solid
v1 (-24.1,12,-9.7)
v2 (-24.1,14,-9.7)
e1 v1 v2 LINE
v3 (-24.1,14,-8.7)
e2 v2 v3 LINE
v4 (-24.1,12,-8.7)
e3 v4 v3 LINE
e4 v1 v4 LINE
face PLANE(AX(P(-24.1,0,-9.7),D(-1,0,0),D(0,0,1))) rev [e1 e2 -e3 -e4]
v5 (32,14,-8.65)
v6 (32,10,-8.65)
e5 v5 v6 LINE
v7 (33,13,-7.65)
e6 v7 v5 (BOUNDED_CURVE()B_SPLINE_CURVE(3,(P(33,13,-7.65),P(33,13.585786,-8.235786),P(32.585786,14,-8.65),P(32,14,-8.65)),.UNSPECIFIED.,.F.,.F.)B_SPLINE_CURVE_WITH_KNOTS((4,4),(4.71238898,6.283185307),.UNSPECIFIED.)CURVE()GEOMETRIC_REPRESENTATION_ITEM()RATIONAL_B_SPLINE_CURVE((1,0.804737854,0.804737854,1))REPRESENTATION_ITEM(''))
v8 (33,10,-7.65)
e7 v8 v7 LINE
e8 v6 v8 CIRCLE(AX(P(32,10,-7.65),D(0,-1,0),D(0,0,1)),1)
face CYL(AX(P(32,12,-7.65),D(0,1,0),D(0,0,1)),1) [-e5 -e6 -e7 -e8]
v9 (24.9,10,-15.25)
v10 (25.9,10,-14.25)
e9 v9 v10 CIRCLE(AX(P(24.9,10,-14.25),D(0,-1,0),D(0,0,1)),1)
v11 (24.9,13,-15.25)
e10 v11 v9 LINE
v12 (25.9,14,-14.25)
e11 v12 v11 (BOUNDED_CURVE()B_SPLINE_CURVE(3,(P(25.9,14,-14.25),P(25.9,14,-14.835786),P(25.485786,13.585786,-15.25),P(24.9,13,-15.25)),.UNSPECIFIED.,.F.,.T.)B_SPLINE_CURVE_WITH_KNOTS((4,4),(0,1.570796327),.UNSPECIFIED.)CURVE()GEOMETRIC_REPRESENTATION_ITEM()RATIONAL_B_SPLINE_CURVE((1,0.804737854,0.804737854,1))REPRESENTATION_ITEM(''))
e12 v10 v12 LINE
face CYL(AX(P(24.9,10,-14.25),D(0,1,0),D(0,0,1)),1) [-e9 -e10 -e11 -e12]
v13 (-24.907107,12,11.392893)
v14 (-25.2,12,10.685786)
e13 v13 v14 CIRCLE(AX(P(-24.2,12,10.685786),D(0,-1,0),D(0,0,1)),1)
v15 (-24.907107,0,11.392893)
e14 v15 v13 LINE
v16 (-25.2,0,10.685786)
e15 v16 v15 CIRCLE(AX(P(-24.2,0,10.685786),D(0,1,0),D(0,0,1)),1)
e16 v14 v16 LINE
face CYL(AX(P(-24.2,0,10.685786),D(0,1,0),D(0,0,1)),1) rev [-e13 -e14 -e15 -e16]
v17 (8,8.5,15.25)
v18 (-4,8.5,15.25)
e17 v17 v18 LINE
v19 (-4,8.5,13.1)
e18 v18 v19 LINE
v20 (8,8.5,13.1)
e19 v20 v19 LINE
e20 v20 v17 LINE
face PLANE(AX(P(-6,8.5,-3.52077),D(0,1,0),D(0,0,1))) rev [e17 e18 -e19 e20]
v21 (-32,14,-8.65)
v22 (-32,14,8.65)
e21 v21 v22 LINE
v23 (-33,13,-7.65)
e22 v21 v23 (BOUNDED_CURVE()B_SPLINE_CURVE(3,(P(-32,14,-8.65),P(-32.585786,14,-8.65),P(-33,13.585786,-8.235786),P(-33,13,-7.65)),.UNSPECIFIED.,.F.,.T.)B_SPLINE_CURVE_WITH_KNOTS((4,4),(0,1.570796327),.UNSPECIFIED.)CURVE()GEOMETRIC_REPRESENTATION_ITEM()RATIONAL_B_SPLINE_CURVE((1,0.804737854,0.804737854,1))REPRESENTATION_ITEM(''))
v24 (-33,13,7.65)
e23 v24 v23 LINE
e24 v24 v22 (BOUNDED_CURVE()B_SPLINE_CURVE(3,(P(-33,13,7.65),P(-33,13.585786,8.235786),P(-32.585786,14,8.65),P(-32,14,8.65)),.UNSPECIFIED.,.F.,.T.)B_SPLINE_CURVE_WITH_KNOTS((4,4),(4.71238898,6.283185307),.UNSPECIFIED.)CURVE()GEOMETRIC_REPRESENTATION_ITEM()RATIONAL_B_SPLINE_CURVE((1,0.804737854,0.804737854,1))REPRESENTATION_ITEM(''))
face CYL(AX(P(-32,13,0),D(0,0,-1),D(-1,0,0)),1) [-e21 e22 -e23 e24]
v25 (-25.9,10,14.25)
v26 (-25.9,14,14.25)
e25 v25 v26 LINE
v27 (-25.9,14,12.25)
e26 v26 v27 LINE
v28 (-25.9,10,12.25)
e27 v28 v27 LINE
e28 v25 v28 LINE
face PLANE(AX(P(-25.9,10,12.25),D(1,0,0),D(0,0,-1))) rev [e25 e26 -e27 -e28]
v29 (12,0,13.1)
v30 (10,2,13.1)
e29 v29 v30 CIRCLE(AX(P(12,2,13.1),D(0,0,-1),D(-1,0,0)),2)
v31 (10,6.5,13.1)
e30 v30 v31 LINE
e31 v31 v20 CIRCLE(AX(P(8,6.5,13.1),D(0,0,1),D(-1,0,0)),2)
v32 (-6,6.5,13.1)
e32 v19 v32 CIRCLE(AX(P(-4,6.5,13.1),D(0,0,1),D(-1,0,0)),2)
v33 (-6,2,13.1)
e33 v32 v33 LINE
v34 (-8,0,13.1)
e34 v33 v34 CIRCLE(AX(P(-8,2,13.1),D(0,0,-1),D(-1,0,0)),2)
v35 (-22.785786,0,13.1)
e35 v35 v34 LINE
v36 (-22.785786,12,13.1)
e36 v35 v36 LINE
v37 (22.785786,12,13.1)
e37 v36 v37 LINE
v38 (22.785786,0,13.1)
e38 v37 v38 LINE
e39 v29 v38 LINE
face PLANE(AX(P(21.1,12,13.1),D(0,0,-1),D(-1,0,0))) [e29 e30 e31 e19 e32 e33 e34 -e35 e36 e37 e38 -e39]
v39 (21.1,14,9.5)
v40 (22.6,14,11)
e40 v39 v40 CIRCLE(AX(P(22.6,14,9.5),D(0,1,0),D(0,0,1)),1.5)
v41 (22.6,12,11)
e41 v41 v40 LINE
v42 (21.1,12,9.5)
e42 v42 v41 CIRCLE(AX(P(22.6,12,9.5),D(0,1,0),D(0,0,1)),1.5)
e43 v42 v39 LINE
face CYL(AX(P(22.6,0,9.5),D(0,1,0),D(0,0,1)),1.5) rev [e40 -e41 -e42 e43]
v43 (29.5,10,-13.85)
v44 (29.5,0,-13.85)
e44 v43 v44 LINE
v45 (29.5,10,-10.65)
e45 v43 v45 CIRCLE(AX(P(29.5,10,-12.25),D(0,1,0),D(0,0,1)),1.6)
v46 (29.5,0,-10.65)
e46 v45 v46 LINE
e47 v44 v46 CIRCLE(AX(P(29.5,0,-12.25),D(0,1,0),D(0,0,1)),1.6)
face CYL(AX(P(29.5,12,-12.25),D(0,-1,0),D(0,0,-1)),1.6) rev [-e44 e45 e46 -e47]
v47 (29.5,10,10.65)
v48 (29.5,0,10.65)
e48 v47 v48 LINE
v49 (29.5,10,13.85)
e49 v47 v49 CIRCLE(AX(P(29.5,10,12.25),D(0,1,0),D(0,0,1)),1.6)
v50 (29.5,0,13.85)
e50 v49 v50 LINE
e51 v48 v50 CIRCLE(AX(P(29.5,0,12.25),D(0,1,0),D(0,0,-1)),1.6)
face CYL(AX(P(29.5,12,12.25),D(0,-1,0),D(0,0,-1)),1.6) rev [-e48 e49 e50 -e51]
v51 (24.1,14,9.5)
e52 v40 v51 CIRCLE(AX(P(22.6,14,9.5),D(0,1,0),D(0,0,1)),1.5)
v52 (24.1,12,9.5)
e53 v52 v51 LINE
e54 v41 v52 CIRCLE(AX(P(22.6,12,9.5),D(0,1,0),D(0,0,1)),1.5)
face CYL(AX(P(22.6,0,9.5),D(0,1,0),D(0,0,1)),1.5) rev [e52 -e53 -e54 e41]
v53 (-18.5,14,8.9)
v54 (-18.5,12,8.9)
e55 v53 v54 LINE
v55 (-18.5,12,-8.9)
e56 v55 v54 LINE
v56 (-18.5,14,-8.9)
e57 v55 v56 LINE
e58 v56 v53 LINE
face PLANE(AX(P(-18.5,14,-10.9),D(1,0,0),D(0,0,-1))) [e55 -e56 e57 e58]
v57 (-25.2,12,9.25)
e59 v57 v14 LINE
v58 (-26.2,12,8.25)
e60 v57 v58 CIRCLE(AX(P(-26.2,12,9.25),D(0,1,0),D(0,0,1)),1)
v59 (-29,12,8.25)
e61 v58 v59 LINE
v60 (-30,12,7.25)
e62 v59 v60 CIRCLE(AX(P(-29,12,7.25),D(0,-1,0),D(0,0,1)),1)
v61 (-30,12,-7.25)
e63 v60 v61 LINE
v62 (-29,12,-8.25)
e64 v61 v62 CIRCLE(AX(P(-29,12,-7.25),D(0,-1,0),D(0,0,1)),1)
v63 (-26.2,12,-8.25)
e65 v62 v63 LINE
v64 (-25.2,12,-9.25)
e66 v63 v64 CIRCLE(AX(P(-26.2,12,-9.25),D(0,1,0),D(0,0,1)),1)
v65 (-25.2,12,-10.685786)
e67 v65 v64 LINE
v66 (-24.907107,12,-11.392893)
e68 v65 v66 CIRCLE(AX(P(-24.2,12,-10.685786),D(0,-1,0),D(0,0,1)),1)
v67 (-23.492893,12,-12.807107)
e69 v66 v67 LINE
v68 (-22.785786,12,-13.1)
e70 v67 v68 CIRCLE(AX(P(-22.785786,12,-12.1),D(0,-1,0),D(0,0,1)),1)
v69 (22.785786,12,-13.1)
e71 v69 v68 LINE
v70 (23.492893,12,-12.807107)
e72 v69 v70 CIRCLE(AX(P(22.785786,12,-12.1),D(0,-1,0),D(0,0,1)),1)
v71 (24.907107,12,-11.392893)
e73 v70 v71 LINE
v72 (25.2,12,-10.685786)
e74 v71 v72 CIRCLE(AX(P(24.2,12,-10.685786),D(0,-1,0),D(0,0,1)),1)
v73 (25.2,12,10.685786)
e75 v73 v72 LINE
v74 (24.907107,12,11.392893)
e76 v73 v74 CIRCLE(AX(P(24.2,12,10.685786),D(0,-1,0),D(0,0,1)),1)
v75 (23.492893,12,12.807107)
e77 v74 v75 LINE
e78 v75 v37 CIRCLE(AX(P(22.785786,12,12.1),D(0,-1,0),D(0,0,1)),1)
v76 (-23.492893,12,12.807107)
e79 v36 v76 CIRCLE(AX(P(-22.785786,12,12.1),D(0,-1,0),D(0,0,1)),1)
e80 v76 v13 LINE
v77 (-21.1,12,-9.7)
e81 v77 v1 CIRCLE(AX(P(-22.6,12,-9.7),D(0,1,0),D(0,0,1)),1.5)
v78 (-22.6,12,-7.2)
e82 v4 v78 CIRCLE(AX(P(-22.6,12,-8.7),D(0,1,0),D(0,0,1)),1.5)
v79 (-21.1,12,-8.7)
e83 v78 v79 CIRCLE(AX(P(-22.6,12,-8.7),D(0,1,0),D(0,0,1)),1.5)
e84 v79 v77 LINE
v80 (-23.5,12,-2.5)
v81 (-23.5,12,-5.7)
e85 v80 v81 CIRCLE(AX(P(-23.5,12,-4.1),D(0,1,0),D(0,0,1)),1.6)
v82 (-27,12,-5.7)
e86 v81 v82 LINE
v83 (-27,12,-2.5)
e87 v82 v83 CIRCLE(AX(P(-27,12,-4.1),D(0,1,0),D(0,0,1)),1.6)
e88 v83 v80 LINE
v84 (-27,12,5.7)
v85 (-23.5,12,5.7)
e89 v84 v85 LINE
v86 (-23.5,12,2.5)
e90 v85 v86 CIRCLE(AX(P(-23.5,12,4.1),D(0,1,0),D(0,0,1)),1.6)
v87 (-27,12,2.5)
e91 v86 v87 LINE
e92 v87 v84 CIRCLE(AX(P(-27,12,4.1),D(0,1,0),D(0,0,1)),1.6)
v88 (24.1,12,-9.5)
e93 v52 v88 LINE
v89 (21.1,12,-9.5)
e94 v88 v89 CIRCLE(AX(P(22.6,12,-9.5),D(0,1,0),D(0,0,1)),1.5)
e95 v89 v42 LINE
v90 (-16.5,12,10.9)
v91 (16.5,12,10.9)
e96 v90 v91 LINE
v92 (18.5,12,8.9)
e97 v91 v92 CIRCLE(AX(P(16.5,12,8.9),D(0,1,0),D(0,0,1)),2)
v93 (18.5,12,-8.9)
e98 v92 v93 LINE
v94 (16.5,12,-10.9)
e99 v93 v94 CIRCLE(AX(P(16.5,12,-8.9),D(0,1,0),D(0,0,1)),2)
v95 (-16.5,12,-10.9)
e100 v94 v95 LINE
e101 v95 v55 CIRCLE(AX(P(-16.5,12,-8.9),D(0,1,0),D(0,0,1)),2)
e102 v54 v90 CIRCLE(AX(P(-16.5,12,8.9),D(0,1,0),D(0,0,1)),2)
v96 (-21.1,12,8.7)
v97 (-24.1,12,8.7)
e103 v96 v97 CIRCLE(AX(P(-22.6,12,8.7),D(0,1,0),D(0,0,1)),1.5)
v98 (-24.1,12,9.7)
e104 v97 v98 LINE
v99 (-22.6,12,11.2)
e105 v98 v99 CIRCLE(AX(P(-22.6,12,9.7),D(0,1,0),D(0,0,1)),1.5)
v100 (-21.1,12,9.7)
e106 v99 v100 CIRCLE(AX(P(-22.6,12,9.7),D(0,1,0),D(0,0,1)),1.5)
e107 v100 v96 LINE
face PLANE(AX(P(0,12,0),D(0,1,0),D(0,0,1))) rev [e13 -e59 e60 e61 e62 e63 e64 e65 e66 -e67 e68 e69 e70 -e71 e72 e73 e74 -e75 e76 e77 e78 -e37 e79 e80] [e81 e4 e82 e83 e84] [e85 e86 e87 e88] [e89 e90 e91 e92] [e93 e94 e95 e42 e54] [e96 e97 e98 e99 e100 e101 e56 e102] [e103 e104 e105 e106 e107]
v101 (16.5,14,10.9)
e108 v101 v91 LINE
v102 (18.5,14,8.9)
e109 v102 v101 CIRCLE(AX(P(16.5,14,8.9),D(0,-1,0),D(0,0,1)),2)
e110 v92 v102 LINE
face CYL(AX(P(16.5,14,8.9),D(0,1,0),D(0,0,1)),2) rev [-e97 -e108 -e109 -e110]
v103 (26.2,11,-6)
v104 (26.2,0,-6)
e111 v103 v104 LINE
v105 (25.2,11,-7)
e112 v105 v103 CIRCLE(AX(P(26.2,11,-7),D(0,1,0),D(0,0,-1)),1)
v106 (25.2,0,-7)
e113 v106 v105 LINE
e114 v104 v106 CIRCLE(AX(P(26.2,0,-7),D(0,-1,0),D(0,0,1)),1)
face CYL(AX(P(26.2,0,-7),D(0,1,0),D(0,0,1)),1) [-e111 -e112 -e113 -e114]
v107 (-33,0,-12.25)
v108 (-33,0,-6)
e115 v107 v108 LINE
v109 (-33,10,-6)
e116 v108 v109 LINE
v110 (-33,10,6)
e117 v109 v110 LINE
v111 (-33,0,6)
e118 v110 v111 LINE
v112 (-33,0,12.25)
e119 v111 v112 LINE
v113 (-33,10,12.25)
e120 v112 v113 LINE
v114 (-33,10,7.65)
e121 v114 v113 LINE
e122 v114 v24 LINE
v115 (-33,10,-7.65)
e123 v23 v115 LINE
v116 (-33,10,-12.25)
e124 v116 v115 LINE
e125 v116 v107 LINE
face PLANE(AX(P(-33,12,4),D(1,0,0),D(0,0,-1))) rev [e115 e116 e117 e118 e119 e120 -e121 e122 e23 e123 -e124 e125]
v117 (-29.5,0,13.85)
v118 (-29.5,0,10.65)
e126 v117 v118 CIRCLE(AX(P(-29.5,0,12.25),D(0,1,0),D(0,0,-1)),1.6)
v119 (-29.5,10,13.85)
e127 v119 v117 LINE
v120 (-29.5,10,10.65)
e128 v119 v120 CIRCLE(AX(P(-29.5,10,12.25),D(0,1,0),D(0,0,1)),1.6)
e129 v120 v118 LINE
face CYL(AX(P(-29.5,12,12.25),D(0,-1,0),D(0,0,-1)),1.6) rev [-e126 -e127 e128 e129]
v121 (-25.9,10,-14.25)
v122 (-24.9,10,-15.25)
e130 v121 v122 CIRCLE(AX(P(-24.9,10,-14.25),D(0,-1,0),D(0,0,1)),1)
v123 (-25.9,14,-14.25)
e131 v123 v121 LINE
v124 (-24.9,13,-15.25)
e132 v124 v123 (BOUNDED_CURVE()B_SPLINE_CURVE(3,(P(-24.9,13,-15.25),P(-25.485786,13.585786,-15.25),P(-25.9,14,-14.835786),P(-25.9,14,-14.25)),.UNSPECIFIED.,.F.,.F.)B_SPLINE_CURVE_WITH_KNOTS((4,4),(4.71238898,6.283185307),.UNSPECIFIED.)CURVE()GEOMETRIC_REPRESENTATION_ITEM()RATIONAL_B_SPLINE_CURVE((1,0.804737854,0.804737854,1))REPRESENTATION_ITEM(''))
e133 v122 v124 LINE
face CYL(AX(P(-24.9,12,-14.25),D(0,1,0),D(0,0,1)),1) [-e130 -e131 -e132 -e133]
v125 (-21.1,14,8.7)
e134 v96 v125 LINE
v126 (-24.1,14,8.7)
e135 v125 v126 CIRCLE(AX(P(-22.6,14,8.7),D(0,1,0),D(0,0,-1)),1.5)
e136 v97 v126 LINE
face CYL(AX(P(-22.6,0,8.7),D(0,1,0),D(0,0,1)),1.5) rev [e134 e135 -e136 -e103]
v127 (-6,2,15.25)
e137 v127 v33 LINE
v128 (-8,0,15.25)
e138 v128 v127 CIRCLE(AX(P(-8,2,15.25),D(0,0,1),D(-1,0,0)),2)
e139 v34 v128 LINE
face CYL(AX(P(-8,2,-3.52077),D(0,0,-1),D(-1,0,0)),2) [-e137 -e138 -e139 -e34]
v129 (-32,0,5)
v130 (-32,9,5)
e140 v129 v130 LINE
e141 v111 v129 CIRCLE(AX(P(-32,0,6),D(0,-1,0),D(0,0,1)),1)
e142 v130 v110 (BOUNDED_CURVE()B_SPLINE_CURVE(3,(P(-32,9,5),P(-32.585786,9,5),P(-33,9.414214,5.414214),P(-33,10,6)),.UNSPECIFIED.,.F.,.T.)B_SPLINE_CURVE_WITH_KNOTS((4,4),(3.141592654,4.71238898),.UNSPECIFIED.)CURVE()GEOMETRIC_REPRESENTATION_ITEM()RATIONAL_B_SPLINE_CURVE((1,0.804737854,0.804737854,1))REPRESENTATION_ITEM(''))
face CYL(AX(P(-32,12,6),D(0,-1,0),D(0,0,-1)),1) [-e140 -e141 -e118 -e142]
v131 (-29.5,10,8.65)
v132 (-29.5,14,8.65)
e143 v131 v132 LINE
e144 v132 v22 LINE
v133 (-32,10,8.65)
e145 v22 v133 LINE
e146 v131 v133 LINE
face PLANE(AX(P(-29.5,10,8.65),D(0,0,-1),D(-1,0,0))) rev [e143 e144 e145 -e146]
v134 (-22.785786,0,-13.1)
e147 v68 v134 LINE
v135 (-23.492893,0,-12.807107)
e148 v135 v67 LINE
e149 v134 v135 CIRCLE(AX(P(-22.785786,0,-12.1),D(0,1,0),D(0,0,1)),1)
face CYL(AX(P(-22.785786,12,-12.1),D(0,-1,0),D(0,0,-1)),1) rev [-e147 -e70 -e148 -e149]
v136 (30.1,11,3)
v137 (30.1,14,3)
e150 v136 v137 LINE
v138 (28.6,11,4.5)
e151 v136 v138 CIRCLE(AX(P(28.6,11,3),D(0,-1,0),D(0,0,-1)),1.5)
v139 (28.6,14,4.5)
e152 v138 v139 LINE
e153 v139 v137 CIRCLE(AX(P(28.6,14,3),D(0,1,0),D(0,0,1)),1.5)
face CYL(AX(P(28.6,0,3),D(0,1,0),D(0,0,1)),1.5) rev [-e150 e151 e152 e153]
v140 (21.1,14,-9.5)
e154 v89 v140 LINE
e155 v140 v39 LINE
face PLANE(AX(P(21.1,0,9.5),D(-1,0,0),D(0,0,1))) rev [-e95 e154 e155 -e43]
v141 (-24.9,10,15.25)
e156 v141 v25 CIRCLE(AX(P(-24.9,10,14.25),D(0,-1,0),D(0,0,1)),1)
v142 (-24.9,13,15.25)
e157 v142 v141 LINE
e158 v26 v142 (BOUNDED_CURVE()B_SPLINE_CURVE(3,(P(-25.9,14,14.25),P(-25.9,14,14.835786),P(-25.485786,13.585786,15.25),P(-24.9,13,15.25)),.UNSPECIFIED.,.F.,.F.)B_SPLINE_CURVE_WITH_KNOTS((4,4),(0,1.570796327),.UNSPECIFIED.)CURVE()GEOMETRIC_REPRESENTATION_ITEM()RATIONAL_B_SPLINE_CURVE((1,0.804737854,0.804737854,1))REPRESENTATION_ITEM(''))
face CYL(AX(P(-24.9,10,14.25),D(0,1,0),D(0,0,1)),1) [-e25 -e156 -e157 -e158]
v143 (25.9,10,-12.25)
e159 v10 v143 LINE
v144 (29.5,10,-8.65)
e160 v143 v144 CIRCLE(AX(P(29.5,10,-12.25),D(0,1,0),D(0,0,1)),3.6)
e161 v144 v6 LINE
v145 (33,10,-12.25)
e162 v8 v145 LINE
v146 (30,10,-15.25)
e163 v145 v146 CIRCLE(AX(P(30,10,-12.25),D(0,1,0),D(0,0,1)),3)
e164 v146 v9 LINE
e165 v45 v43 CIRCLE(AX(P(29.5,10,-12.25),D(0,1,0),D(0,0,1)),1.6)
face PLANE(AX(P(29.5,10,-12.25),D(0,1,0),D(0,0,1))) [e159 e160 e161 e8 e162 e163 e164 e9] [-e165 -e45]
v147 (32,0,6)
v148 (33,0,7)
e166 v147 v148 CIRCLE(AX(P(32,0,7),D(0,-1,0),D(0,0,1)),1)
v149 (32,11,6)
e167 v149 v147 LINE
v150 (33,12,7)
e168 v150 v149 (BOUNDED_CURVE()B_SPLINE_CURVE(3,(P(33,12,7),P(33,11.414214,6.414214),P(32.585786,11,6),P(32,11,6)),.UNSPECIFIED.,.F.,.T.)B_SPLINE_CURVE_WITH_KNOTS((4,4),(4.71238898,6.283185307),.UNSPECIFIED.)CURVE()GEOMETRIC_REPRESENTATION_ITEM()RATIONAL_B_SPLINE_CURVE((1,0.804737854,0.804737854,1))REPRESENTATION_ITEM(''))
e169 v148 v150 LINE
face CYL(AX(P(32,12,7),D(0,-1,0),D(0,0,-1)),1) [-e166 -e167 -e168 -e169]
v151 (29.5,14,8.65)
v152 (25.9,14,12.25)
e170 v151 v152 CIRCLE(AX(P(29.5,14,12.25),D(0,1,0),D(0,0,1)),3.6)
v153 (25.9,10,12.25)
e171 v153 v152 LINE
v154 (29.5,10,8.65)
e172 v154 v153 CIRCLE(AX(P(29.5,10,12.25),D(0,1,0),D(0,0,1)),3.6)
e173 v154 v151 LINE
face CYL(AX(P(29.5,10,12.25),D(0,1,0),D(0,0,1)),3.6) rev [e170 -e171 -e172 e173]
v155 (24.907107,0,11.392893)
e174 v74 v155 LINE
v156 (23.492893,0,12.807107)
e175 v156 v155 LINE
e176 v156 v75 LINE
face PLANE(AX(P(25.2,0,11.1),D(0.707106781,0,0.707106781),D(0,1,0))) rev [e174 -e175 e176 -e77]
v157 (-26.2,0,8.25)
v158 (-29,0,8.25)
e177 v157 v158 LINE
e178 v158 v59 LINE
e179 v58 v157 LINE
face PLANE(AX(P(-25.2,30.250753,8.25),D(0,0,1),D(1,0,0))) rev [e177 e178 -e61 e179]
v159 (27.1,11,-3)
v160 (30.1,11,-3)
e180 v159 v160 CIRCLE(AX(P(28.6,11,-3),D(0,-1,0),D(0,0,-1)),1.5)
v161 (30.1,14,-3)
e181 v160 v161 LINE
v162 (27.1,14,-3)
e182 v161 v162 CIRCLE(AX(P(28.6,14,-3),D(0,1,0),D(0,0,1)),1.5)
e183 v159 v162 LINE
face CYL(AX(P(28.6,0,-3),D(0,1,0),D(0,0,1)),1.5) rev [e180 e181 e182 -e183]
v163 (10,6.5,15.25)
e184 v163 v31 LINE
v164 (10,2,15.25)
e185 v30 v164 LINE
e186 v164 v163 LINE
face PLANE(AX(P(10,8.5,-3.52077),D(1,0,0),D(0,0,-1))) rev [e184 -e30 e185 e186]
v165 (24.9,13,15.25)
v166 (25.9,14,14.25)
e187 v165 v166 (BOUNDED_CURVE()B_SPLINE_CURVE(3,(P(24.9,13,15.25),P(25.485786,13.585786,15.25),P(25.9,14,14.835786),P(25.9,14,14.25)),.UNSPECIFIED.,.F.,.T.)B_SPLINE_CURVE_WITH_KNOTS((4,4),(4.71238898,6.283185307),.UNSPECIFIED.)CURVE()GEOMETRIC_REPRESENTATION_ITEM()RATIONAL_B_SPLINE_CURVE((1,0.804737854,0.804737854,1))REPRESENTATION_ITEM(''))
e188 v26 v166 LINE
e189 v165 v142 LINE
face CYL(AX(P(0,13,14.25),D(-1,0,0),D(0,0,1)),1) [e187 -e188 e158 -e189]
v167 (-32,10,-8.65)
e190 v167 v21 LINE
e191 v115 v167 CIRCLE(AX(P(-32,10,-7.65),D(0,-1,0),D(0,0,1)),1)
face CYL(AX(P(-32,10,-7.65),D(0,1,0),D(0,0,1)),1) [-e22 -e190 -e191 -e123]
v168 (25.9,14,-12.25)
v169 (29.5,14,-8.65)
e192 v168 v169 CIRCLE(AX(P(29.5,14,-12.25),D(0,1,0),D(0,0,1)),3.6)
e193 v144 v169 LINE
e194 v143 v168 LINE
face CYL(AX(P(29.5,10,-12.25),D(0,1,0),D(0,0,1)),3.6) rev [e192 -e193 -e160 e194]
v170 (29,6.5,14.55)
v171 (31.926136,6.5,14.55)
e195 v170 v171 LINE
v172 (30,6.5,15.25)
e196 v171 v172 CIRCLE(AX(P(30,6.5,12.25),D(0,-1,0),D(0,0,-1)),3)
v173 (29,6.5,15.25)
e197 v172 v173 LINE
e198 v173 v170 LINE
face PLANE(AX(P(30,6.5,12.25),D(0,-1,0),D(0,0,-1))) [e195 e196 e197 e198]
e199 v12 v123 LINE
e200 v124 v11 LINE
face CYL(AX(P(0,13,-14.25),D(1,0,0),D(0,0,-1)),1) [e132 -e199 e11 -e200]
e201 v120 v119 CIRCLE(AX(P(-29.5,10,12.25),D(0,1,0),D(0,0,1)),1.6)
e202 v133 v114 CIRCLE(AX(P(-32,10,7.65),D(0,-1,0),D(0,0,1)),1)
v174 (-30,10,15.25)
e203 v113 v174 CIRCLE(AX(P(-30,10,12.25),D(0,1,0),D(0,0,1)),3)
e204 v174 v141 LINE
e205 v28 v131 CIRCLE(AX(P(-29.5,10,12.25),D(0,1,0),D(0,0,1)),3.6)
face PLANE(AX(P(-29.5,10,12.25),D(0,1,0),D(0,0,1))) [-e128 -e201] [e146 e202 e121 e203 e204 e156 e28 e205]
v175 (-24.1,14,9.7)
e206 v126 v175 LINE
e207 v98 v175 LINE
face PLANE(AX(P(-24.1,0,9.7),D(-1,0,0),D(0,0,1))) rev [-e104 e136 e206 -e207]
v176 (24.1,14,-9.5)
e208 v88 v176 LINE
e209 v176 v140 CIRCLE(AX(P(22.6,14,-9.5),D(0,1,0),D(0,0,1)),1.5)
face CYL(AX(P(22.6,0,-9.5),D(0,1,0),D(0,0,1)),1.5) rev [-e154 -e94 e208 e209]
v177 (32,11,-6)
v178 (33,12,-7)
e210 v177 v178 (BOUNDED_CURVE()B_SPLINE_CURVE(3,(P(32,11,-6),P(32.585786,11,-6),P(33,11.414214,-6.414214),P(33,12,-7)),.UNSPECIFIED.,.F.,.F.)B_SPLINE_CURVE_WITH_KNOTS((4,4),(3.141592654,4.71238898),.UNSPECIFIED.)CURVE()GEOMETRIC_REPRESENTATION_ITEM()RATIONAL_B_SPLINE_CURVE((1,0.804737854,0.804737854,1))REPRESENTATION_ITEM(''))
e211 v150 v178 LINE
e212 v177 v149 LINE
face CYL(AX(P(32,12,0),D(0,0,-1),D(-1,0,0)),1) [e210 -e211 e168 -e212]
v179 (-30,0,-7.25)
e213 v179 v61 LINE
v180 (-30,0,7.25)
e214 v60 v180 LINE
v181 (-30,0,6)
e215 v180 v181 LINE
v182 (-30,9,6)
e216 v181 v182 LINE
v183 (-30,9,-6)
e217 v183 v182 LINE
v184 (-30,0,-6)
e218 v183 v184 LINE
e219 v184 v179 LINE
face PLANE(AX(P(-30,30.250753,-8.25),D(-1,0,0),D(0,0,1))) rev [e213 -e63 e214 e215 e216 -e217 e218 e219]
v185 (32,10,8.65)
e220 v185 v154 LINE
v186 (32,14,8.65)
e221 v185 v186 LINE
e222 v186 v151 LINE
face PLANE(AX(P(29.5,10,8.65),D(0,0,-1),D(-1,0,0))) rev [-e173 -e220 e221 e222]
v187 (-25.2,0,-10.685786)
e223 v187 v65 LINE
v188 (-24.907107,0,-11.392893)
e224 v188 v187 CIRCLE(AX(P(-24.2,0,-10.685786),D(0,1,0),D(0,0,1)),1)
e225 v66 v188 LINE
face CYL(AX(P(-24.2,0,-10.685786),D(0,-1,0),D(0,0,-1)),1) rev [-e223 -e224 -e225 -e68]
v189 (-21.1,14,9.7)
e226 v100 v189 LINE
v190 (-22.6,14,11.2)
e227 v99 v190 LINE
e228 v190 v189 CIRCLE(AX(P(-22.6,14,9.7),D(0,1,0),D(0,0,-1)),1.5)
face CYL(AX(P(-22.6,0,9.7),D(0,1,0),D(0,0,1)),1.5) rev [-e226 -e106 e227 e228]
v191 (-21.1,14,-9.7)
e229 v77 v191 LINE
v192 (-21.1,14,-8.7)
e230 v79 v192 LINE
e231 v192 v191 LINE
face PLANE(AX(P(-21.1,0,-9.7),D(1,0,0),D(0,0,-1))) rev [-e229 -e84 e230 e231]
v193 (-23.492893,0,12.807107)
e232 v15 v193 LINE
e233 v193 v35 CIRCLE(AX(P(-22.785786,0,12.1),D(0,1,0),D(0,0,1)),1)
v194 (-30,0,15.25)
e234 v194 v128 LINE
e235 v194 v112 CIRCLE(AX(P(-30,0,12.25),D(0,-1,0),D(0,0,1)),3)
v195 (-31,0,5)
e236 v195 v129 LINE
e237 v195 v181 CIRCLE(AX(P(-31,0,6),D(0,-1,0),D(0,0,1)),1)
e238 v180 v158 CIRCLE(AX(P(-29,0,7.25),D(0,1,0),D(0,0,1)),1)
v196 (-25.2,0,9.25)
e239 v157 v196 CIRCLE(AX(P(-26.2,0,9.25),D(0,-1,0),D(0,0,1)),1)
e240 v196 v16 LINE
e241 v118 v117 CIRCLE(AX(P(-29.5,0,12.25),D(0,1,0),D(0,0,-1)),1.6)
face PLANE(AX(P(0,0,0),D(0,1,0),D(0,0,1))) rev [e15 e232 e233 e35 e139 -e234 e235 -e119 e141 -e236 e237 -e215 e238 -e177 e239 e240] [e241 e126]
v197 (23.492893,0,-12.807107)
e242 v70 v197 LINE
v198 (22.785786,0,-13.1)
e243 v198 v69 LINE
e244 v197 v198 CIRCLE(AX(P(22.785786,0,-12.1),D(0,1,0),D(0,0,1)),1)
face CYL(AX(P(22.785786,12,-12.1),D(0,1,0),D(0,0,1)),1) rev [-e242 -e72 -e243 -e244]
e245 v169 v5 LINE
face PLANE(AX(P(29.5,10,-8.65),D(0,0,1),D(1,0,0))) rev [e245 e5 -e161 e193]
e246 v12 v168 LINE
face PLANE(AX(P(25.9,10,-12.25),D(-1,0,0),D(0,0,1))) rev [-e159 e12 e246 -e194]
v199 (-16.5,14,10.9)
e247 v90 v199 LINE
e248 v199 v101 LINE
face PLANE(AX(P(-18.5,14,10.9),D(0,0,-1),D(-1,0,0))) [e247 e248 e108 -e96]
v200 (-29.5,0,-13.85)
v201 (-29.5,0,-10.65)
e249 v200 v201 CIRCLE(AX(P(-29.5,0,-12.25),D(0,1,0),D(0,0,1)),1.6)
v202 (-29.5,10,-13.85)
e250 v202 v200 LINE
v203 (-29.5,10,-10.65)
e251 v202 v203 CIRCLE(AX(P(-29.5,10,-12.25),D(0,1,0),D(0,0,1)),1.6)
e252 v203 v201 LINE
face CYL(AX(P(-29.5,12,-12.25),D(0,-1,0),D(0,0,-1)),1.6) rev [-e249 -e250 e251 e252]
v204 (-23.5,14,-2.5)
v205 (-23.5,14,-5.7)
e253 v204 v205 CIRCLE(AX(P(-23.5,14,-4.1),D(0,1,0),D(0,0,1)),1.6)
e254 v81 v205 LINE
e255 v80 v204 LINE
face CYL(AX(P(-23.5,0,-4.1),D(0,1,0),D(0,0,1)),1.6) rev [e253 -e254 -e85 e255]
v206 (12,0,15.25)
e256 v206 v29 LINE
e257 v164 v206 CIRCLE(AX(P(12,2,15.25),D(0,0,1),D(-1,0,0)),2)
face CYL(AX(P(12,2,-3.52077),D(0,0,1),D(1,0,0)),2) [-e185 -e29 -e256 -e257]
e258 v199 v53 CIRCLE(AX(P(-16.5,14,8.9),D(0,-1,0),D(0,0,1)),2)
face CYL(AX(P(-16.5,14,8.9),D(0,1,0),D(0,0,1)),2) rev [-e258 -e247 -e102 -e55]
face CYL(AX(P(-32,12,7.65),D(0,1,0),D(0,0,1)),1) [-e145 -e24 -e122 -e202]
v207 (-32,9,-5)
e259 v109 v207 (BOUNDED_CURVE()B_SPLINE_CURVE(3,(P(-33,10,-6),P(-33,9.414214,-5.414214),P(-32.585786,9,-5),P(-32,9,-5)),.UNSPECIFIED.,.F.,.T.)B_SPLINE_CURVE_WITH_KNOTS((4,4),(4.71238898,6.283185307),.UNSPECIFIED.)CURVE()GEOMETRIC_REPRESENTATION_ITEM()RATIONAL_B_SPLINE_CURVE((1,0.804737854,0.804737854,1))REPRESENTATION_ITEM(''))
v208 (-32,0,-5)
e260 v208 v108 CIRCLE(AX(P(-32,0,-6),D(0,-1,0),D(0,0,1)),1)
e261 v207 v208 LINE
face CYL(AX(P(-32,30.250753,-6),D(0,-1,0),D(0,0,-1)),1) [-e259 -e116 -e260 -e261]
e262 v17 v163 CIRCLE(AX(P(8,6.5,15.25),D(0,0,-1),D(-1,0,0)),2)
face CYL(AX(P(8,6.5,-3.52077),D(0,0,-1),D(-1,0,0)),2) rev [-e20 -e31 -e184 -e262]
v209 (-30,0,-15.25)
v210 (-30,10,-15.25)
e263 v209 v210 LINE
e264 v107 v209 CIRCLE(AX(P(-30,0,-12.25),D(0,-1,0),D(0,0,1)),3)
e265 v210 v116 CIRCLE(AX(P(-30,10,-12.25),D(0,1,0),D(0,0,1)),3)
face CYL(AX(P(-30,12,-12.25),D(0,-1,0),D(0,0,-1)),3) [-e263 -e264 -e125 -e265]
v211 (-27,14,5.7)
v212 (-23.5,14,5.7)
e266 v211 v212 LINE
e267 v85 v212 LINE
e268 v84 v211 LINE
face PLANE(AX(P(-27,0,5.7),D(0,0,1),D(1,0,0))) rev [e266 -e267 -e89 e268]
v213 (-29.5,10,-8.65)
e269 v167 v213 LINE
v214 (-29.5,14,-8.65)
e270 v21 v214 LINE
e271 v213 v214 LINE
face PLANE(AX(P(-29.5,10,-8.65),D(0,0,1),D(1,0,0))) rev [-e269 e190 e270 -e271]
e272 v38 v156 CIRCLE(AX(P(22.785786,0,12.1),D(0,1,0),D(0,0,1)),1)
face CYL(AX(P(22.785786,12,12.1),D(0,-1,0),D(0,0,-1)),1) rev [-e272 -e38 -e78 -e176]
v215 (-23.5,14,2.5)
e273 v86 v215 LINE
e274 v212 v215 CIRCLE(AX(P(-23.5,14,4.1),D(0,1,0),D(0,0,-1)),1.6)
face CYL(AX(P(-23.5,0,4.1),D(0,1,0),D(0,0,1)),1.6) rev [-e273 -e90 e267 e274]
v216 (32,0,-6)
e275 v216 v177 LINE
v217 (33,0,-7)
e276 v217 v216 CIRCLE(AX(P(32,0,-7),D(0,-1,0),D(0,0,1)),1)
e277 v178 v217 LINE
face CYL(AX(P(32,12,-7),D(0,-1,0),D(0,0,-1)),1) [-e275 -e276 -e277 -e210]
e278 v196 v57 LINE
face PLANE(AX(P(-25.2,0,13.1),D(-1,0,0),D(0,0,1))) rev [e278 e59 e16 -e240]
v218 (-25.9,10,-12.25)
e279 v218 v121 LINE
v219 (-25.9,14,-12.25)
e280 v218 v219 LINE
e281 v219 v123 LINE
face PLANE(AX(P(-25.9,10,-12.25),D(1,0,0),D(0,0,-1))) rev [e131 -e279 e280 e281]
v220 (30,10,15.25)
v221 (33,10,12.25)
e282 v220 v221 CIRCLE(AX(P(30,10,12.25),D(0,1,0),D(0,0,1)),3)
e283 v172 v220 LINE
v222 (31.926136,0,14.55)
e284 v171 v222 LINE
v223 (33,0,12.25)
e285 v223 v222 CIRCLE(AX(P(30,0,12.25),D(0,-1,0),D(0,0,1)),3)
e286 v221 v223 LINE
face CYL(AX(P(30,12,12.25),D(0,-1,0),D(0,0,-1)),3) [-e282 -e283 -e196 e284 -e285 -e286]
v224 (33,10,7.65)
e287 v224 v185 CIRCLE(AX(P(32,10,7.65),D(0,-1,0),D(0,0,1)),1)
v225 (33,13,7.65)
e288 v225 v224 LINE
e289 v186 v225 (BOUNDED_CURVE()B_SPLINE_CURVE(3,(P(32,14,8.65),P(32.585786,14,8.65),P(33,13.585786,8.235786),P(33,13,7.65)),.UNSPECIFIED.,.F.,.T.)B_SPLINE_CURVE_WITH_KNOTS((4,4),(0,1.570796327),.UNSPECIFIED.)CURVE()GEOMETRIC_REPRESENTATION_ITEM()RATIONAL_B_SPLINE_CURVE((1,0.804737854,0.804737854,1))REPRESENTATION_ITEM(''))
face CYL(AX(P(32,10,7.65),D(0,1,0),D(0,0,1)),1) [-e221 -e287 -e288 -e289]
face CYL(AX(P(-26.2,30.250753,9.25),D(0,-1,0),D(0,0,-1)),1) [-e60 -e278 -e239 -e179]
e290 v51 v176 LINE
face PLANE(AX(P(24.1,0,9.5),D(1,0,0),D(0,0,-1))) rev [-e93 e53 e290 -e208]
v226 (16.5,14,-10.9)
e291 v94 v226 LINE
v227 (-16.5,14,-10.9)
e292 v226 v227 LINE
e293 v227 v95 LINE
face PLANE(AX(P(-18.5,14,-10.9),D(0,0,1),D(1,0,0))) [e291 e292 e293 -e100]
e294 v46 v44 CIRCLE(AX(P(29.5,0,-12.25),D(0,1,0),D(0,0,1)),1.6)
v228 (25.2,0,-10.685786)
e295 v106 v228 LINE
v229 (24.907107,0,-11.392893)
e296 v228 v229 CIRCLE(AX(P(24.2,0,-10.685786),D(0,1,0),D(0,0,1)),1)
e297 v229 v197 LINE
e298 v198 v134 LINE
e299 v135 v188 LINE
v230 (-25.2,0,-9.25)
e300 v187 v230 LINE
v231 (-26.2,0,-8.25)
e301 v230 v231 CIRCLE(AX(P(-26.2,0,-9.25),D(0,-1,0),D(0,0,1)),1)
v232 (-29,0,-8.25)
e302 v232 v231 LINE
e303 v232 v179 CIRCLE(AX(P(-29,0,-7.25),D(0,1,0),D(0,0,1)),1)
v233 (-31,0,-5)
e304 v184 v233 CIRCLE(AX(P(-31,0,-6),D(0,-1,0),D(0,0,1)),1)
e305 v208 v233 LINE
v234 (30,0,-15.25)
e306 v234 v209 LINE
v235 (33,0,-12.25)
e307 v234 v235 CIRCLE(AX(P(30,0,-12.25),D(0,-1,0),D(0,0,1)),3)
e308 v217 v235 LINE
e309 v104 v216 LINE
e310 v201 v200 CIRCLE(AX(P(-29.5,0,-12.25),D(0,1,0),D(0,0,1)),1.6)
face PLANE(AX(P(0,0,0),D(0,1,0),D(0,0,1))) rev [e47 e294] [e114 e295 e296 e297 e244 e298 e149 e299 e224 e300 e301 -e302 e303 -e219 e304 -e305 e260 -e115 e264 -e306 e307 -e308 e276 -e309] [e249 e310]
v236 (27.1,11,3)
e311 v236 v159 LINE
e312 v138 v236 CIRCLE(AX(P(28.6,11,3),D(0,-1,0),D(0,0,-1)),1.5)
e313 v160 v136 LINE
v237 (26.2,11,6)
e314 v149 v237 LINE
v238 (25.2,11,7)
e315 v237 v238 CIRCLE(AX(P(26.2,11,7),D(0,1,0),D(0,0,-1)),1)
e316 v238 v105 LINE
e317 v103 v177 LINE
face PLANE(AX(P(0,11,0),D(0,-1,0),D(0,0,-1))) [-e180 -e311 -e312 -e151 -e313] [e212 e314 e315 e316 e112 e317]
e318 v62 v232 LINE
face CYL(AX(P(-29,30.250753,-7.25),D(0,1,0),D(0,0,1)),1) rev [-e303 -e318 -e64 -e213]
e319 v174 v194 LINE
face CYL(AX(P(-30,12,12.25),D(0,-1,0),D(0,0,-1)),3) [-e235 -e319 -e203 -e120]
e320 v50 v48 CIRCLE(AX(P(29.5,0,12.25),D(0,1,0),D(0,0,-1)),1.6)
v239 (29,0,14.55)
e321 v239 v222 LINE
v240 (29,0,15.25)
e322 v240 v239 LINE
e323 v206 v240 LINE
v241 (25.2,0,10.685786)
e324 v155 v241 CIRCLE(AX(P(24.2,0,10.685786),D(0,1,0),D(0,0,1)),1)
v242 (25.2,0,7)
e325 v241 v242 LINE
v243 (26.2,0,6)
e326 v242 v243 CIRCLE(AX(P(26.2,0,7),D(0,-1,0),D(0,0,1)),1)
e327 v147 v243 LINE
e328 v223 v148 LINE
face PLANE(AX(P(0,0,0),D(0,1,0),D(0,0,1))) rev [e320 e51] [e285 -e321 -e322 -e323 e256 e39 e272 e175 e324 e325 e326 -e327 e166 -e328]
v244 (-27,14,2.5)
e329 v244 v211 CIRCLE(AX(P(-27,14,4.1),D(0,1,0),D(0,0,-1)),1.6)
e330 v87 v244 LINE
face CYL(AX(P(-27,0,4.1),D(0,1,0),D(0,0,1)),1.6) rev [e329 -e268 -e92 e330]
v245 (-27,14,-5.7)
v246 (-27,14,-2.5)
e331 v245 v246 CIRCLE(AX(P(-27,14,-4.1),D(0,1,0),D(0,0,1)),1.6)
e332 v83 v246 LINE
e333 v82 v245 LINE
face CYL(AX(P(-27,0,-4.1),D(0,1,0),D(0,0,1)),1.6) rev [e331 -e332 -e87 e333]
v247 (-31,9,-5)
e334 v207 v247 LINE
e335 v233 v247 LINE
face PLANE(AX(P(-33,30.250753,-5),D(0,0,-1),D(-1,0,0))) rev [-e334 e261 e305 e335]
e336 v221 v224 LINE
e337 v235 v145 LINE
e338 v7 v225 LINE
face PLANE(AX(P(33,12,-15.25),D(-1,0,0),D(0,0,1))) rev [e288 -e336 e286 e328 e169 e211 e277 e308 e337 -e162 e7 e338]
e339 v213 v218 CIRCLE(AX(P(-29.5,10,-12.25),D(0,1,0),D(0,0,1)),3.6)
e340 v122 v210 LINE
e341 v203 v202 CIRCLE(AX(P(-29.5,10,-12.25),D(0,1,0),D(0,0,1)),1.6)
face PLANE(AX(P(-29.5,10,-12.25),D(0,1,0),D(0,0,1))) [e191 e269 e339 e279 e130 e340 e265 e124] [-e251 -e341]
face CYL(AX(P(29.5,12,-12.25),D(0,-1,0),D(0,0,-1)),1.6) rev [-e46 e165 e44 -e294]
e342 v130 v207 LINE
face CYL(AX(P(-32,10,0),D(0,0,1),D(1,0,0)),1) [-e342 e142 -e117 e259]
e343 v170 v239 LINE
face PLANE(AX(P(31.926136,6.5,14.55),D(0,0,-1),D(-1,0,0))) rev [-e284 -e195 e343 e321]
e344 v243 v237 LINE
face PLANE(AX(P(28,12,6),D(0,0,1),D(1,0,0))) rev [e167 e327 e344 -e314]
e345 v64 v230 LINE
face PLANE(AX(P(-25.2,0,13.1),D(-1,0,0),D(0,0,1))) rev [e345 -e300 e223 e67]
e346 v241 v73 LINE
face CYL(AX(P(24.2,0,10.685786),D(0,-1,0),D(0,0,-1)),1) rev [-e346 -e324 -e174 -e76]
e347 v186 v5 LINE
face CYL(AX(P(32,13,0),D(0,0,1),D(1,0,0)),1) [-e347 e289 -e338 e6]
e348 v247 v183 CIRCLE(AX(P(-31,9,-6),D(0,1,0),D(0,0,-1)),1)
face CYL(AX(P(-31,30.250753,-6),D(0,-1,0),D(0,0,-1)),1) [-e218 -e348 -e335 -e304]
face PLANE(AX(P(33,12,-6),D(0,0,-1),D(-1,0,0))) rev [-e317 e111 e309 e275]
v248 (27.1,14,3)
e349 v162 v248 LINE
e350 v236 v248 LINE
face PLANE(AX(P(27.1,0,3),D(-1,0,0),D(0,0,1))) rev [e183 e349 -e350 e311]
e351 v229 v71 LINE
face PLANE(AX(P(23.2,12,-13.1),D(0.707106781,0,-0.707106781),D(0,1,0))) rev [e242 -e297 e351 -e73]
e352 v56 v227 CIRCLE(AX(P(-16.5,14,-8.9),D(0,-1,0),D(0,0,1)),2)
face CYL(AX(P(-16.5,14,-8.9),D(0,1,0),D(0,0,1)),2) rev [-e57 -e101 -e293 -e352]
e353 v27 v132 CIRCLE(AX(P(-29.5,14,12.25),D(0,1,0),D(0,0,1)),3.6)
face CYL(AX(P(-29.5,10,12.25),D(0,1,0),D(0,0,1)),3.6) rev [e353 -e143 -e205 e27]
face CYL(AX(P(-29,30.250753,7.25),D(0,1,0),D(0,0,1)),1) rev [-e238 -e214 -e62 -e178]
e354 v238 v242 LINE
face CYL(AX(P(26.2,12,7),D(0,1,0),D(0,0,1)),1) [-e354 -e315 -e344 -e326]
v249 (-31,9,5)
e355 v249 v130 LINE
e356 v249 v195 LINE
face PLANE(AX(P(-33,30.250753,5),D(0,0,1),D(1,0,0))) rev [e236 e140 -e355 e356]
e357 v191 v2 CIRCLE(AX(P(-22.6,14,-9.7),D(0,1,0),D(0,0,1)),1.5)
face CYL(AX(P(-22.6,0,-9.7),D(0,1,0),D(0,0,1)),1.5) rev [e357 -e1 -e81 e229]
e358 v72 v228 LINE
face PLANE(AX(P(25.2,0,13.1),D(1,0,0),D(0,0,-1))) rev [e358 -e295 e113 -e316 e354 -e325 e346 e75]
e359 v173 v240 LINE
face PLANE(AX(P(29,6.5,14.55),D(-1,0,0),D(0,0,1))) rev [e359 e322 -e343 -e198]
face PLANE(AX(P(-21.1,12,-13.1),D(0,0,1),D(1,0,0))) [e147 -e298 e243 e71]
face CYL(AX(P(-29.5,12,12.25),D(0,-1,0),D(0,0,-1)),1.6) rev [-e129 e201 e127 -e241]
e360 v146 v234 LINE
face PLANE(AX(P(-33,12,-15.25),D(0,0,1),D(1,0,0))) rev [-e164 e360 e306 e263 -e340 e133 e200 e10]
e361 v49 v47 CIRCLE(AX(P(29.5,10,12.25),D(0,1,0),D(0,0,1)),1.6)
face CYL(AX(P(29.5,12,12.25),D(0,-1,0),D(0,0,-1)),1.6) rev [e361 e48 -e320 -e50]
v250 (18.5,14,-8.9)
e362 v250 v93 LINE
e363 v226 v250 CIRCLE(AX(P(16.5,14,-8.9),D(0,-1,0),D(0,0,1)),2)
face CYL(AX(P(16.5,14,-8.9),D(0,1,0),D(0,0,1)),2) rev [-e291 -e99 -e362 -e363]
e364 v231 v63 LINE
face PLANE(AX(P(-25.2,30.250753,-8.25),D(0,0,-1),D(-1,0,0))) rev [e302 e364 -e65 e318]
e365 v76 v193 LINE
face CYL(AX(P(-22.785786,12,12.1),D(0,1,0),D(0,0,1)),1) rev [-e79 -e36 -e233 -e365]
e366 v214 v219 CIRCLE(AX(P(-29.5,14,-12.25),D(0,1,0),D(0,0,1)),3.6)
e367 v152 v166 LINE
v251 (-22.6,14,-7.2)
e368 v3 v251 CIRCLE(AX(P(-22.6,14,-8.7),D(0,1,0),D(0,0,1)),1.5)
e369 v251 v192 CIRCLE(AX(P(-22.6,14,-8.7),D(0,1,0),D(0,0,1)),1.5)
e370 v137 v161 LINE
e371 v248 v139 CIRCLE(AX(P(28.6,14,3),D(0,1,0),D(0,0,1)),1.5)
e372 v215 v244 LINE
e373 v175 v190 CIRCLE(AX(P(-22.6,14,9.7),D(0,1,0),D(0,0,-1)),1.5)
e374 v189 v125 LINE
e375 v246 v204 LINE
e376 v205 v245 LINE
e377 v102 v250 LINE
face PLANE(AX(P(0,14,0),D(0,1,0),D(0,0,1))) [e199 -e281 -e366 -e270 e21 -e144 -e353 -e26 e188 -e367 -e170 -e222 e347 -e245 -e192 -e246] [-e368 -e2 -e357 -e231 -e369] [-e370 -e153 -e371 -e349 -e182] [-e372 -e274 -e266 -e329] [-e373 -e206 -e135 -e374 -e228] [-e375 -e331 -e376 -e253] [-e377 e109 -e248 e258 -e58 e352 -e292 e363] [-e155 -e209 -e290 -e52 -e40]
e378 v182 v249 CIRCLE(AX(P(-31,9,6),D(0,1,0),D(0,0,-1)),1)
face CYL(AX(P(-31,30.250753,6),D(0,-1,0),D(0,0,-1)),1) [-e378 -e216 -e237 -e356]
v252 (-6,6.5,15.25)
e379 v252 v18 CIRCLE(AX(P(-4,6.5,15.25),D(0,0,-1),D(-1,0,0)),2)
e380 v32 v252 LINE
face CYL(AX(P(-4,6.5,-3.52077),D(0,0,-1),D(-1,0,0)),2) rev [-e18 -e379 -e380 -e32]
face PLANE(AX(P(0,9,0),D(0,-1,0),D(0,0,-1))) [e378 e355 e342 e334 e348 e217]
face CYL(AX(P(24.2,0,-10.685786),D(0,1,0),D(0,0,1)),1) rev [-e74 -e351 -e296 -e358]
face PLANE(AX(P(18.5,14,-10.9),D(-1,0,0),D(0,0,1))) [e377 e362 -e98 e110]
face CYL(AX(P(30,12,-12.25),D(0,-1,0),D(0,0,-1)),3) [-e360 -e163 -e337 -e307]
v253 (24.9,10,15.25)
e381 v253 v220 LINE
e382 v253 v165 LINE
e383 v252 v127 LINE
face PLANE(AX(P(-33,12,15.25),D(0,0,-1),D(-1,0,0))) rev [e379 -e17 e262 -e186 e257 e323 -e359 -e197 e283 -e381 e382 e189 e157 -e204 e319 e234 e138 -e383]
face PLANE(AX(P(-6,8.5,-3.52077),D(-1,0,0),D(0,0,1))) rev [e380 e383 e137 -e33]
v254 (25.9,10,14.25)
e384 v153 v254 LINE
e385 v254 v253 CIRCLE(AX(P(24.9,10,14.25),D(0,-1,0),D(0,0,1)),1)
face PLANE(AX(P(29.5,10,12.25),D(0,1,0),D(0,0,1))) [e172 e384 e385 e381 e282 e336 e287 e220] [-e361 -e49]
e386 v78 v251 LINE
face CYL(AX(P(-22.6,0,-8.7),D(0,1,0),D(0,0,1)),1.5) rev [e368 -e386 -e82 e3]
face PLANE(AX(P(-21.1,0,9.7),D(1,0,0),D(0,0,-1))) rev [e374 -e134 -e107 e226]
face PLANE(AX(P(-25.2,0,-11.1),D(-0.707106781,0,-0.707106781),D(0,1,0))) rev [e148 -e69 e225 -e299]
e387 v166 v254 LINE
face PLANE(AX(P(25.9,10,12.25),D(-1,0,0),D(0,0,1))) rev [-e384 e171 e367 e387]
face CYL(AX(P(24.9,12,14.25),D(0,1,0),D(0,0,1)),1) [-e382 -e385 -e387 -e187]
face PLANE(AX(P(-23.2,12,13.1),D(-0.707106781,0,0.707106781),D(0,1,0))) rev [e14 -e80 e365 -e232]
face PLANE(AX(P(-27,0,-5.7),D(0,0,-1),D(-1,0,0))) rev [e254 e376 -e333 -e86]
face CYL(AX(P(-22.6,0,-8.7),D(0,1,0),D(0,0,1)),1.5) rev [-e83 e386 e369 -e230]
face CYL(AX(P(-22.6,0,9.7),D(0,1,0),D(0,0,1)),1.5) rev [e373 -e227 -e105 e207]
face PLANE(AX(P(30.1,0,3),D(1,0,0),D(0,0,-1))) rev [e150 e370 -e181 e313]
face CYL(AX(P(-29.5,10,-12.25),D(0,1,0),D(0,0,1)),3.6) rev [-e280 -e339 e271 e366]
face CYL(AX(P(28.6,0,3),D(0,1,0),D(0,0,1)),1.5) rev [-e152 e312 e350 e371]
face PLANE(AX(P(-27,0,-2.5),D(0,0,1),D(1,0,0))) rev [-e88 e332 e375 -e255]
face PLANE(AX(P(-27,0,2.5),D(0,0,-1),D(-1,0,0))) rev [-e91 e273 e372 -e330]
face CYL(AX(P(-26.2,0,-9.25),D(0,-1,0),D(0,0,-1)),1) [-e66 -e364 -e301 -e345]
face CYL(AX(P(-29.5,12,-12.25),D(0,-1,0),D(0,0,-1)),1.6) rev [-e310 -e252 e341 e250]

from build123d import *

# Parameters (mm, degrees)
SKETCH_1_R           = 1.6
EXTRUDE_1_DEPTH      = 12
SKETCH_2_W           = 52
SKETCH_2_H           = 26.2
CUT_EXTRUDE_1_DEPTH  = 2
SKETCH_3_W           = 7.4
SKETCH_3_H           = 20
CUT_EXTRUDE_2_DEPTH  = 8
SKETCH_4_W           = 16
SKETCH_4_H           = 4.5
CUT_EXTRUDE_3_DEPTH  = 2.15
SKETCH_5_W           = 52
SKETCH_5_H           = 26.2
CUT_EXTRUDE_4_DEPTH  = 39.28266579
SKETCH_6_W           = 66
SKETCH_6_H           = 30.5
SKETCH_6_R           = 1.6
SKETCH_6_W_2         = 37
SKETCH_6_H_2         = 21.8
EXTRUDE_2_DEPTH      = 2
SKETCH_7_W           = 2
SKETCH_7_H           = 12
SKETCH_7_W_2         = 1.6
SKETCH_7_H_2         = 8
CUT_EXTRUDE_5_DEPTH  = 39.28266579
SKETCH_8_W           = 16
SKETCH_8_H           = 2.15
CUT_EXTRUDE_6_DEPTH  = 38.33379836
SKETCH_9_W           = 0.8
SKETCH_9_H           = 7.1
EXTRUDE_3_DEPTH      = 12
CUT_EXTRUDE_7_DEPTH  = 12
SKETCH_11_W          = 3
SKETCH_11_H          = 10
EXTRUDE_4_DEPTH      = 3
SKETCH_13_W          = 7.8
SKETCH_13_H          = 12
EXTRUDE_5_DEPTH      = 1
CHAMFER_1_SIZE       = 2
CUT_EXTRUDE_8_DEPTH  = 4
CUT_EXTRUDE_9_DEPTH  = 39.955904559
FILLET_R1_R          = 1
FILLET_R2_R          = 2
FILLET_R3_R          = 3
CUT_EXTRUDE_START    = -6.5
CUT_EXTRUDE_10_DEPTH = 6.5


with BuildPart() as part:
    # 草图1 → 凸台-拉伸1 (new body)
    with BuildSketch(Plane(origin=(0, 0, 0), x_dir=(1, 0, 0), z_dir=(0, 1, 0))):
        Polygon((-33, 4), (-27.6, 4), (-27.6, -4), (-33, -4), (-33, -15.25), (33, -15.25), (33, -6), (28, -6), (28, 6), (33, 6), (33, 15.25), (-33, 15.25), align=None)
        with Locations(Location((-29.5, 12.25, 0), (0, 0, 270))):
            Circle(SKETCH_1_R, mode=Mode.SUBTRACT)
        with Locations(Location((29.5, 12.25, 0), (0, 0, 270))):
            Circle(SKETCH_1_R, mode=Mode.SUBTRACT)
        with Locations(Location((-29.5, -12.25, 0), (0, 0, 90))):
            Circle(SKETCH_1_R, mode=Mode.SUBTRACT)
        with Locations(Location((29.5, -12.25, 0), (0, 0, 90))):
            Circle(SKETCH_1_R, mode=Mode.SUBTRACT)
        Polygon((-26, -5.75), (-26, 5.75), (-21.1, 5.75), (-21.1, 13.1), (21.1, 13.1), (21.1, -13.1), (-21.1, -13.1), (-21.1, -5.75), align=None, mode=Mode.SUBTRACT)
    extrude(amount=EXTRUDE_1_DEPTH)

    # 草图2 → 切除-拉伸1 (cut)
    with BuildSketch(Plane.XZ):
        Rectangle(SKETCH_2_W, SKETCH_2_H)
    extrude(amount=-CUT_EXTRUDE_1_DEPTH, mode=Mode.SUBTRACT)

    # 草图3 → 切除-拉伸2 (cut)
    with BuildSketch(Plane(origin=(0, 12, 0), x_dir=(1, 0, 0), z_dir=(0, 1, 0))):
        with Locations((-26.8, 0)):
            Rectangle(SKETCH_3_W, SKETCH_3_H)
        Polygon((28, -6), (28, 6), (26, 6), (26, 13.1), (21.1, 13.1), (21.1, -13.1), (26, -13.1), (26, -6), align=None)
    extrude(amount=-CUT_EXTRUDE_2_DEPTH, mode=Mode.SUBTRACT)

    # 草图4 → 切除-拉伸3 (cut)
    with BuildSketch(Plane.XY.offset(15.25)):
        with Locations((2, 6.25)):
            Rectangle(SKETCH_4_W, SKETCH_4_H)
    extrude(amount=-CUT_EXTRUDE_3_DEPTH, mode=Mode.SUBTRACT)

    # 草图5 → 切除-拉伸4 (cut, through all)
    with BuildSketch(Plane.XZ):
        Rectangle(SKETCH_5_W, SKETCH_5_H)
    extrude(amount=-CUT_EXTRUDE_4_DEPTH, mode=Mode.SUBTRACT)

    # 草图6 → 凸台-拉伸2 (add)
    with BuildSketch(Plane(origin=(0, 12, 0), x_dir=(1, 0, 0), z_dir=(0, 1, 0))):
        Rectangle(SKETCH_6_W, SKETCH_6_H)
        with Locations(Location((-29.5, -12.25, 0), (0, 0, 90))):
            Circle(SKETCH_6_R, mode=Mode.SUBTRACT)
        with Locations(Location((29.5, -12.25, 0), (0, 0, 90))):
            Circle(SKETCH_6_R, mode=Mode.SUBTRACT)
        with Locations(Location((29.5, 12.25, 0), (0, 0, 270))):
            Circle(SKETCH_6_R, mode=Mode.SUBTRACT)
        with Locations(Location((-29.5, 12.25, 0), (0, 0, 270))):
            Circle(SKETCH_6_R, mode=Mode.SUBTRACT)
        Rectangle(SKETCH_6_W_2, SKETCH_6_H_2, mode=Mode.SUBTRACT)
    extrude(amount=EXTRUDE_2_DEPTH)

    # 草图7 → 切除-拉伸5 (cut, through all)
    with BuildSketch(Plane.XZ.offset(-12)):
        with Locations((27, 0)):
            Rectangle(SKETCH_7_W, SKETCH_7_H)
        with Locations((-26.8, 0)):
            Rectangle(SKETCH_7_W_2, SKETCH_7_H_2)
    extrude(amount=CUT_EXTRUDE_5_DEPTH, mode=Mode.SUBTRACT)

    # 草图8 → 切除-拉伸6 (cut, through all)
    with BuildSketch(Plane.XZ.offset(-8.5)):
        with Locations((2, 14.175)):
            Rectangle(SKETCH_8_W, SKETCH_8_H)
    extrude(amount=CUT_EXTRUDE_6_DEPTH, mode=Mode.SUBTRACT)

    # 草图9 → 凸台-拉伸3 (add, through all)
    with BuildSketch(Plane.XZ.offset(-12)):
        with Locations((25.6, 9.55)):
            Rectangle(SKETCH_9_W, SKETCH_9_H)
        Polygon((-25.2, -13.1), (-26, -13.1), (-26, -10), (-30.5, -10), (-30.5, -4), (-33, -4), (-33, 4), (-30.5, 4), (-30.5, 10), (-26, 10), (-26, 13.1), (-25.2, 13.1), align=None)
        with Locations((25.6, -9.55)):
            Rectangle(SKETCH_9_W, SKETCH_9_H)
    extrude(amount=EXTRUDE_3_DEPTH)

    # 草图10 → 切除-拉伸7 (cut)
    with BuildSketch(Plane.XZ):
        Polygon((-33, -5), (-33, 5), (-30, 5), (-30, 8.25), (-25.2, 8.25), (-25.2, -8.25), (-30, -8.25), (-30, -5), align=None)
    extrude(amount=-CUT_EXTRUDE_7_DEPTH, mode=Mode.SUBTRACT)

    # 草图11 → 凸台-拉伸4 (add)
    with BuildSketch(Plane.XZ.offset(-12)):
        with Locations((-31.5, 0)):
            Rectangle(SKETCH_11_W, SKETCH_11_H)
    extrude(amount=EXTRUDE_4_DEPTH)

    # 草图13 → 凸台-拉伸5 (add)
    with BuildSketch(Plane.XZ.offset(-12)):
        with Locations((29.1, 0)):
            Rectangle(SKETCH_13_W, SKETCH_13_H)
    extrude(amount=EXTRUDE_5_DEPTH)

    # 倒角1
    chamfer_1_edges = [part.edges().sort_by_distance(p)[0] for p in [
        (-25.2, 6, -13.1),
        (-25.2, 6, 13.1),
        (25.2, 6, 13.1),
        (25.2, 6, -13.1),
    ]]
    chamfer(chamfer_1_edges, length=CHAMFER_1_SIZE)

    # 草图12 → 切除-拉伸8 (cut)
    with BuildSketch(Plane(origin=(0, 14, 0), x_dir=(1, 0, 0), z_dir=(0, 1, 0))):
        with BuildLine():
            Line((-29.5, 8.65), (-33, 8.65))
            Line((-33, 8.65), (-33, 15.25))
            Line((-33, 15.25), (-25.9, 15.25))
            Line((-25.9, 15.25), (-25.9, 12.25))
            ThreePointArc((-25.9, 12.25), (-26.954415588, 9.704415588), (-29.5, 8.65))
        make_face()
        with BuildLine():
            Line((29.5, 8.65), (33, 8.65))
            Line((33, 8.65), (33, 15.25))
            Line((33, 15.25), (25.9, 15.25))
            Line((25.9, 15.25), (25.9, 12.25))
            ThreePointArc((25.9, 12.25), (26.954415588, 9.704415588), (29.5, 8.65))
        make_face()
        with BuildLine():
            Line((29.5, -8.65), (33, -8.65))
            Line((33, -8.65), (33, -15.25))
            Line((33, -15.25), (25.9, -15.25))
            Line((25.9, -15.25), (25.9, -12.25))
            ThreePointArc((25.9, -12.25), (26.954415588, -9.704415588), (29.5, -8.65))
        make_face()
        with BuildLine():
            Line((-25.9, -12.25), (-25.9, -15.25))
            Line((-25.9, -15.25), (-33, -15.25))
            Line((-33, -15.25), (-33, -8.65))
            Line((-33, -8.65), (-29.5, -8.65))
            ThreePointArc((-29.5, -8.65), (-26.954415588, -9.704415588), (-25.9, -12.25))
        make_face()
    extrude(amount=-CUT_EXTRUDE_8_DEPTH, mode=Mode.SUBTRACT)

    # 草图14 → 切除-拉伸9 (cut, through all)
    with BuildSketch(Plane(origin=(0, 14, 0), x_dir=(1, 0, 0), z_dir=(0, 1, 0))):
        with BuildLine():
            Line((21.1, -9.5), (21.1, 9.5))
            ThreePointArc((21.1, 9.5), (22.6, 11), (24.1, 9.5))
            Line((24.1, 9.5), (24.1, -9.5))
            ThreePointArc((24.1, -9.5), (22.6, -11), (21.1, -9.5))
        make_face()
        with BuildLine():
            Line((27.1, -3), (27.1, 3))
            ThreePointArc((27.1, 3), (28.6, 4.5), (30.1, 3))
            Line((30.1, 3), (30.1, -3))
            ThreePointArc((30.1, -3), (28.6, -4.5), (27.1, -3))
        make_face()
        with BuildLine():
            Line((-27, 5.7), (-23.5, 5.7))
            ThreePointArc((-23.5, 5.7), (-21.9, 4.1), (-23.5, 2.5))
            Line((-23.5, 2.5), (-27, 2.5))
            ThreePointArc((-27, 2.5), (-28.6, 4.1), (-27, 5.7))
        make_face()
        with BuildLine():
            Line((-27, -5.7), (-23.5, -5.7))
            ThreePointArc((-23.5, -5.7), (-21.9, -4.1), (-23.5, -2.5))
            Line((-23.5, -2.5), (-27, -2.5))
            ThreePointArc((-27, -2.5), (-28.6, -4.1), (-27, -5.7))
        make_face()
        with BuildLine():
            Line((-21.1, 9.7), (-21.1, 8.7))
            ThreePointArc((-21.1, 8.7), (-22.6, 7.2), (-24.1, 8.7))
            Line((-24.1, 8.7), (-24.1, 9.7))
            ThreePointArc((-24.1, 9.7), (-22.6, 11.2), (-21.1, 9.7))
        make_face()
        with BuildLine():
            Line((-21.1, -9.7), (-21.1, -8.7))
            ThreePointArc((-21.1, -8.7), (-22.6, -7.2), (-24.1, -8.7))
            Line((-24.1, -8.7), (-24.1, -9.7))
            ThreePointArc((-24.1, -9.7), (-22.6, -11.2), (-21.1, -9.7))
        make_face()
    extrude(amount=-CUT_EXTRUDE_9_DEPTH, mode=Mode.SUBTRACT)

    # R1 过渡圆角
    fillet_r1_edges = [part.edges().sort_by_distance(p)[0] for p in [
        (25.2, 5.5, 6),
        (25.2, 5.5, -6),
        (-30, 6, -8.25),
        (-25.2, 6, -8.25),
        (-25.2, 6, 8.25),
        (-30, 6, 8.25),
        (-30, 4.5, 5),
        (-33, 4.5, 5),
        (-30, 4.5, -5),
        (-33, 4.5, -5),
        (-33, 9, 0),
        (33, 5.5, 6),
        (33, 5.5, -6),
        (33, 11, 0),
        (-25.2, 6, -11.1),
        (23.2, 6, -13.1),
        (-23.2, 6, -13.1),
        (25.2, 6, 11.1),
        (25.2, 6, -11.1),
        (-23.2, 6, 13.1),
        (23.2, 6, 13.1),
        (-25.2, 6, 11.1),
        (0, 14, -15.25),
        (-33, 14, 0),
        (0, 14, 15.25),
        (33, 14, 0),
        (33, 12, 8.65),
        (25.9, 12, 15.25),
        (-25.9, 12, 15.25),
        (-33, 12, 8.65),
        (-33, 12, -8.65),
        (-25.9, 12, -15.25),
        (25.9, 12, -15.25),
        (33, 12, -8.65),
    ]]
    fillet(fillet_r1_edges, radius=FILLET_R1_R)

    # R2 过渡圆角
    fillet_r2_edges = [part.edges().sort_by_distance(p)[0] for p in [
        (10, 8.5, 14.175),
        (-6, 8.5, 14.175),
        (-18.5, 13, 10.9),
        (18.5, 13, 10.9),
        (18.5, 13, -10.9),
        (-18.5, 13, -10.9),
        (10, 0, 14.175),
        (-6, 0, 14.175),
    ]]
    fillet(fillet_r2_edges, radius=FILLET_R2_R)

    # R3 过渡圆角
    fillet_r3_edges = [part.edges().sort_by_distance(p)[0] for p in [
        (-33, 5, 15.25),
        (-33, 5, -15.25),
        (33, 5, -15.25),
        (33, 5, 15.25),
    ]]
    fillet(fillet_r3_edges, radius=FILLET_R3_R)

    # 草图15 → 切除-拉伸10 (cut)
    with BuildSketch(Plane.XZ.offset(CUT_EXTRUDE_START)):
        with BuildLine():
            Line((29, 15.25), (30, 15.25))
            ThreePointArc((30, 15.25), (31.024695077, 15.069574436), (31.926136028, 14.55))
            Line((31.926136028, 14.55), (29, 14.55))
            Line((29, 14.55), (29, 15.25))
        make_face()
    extrude(amount=CUT_EXTRUDE_10_DEPTH, mode=Mode.SUBTRACT)


solid = part.part
